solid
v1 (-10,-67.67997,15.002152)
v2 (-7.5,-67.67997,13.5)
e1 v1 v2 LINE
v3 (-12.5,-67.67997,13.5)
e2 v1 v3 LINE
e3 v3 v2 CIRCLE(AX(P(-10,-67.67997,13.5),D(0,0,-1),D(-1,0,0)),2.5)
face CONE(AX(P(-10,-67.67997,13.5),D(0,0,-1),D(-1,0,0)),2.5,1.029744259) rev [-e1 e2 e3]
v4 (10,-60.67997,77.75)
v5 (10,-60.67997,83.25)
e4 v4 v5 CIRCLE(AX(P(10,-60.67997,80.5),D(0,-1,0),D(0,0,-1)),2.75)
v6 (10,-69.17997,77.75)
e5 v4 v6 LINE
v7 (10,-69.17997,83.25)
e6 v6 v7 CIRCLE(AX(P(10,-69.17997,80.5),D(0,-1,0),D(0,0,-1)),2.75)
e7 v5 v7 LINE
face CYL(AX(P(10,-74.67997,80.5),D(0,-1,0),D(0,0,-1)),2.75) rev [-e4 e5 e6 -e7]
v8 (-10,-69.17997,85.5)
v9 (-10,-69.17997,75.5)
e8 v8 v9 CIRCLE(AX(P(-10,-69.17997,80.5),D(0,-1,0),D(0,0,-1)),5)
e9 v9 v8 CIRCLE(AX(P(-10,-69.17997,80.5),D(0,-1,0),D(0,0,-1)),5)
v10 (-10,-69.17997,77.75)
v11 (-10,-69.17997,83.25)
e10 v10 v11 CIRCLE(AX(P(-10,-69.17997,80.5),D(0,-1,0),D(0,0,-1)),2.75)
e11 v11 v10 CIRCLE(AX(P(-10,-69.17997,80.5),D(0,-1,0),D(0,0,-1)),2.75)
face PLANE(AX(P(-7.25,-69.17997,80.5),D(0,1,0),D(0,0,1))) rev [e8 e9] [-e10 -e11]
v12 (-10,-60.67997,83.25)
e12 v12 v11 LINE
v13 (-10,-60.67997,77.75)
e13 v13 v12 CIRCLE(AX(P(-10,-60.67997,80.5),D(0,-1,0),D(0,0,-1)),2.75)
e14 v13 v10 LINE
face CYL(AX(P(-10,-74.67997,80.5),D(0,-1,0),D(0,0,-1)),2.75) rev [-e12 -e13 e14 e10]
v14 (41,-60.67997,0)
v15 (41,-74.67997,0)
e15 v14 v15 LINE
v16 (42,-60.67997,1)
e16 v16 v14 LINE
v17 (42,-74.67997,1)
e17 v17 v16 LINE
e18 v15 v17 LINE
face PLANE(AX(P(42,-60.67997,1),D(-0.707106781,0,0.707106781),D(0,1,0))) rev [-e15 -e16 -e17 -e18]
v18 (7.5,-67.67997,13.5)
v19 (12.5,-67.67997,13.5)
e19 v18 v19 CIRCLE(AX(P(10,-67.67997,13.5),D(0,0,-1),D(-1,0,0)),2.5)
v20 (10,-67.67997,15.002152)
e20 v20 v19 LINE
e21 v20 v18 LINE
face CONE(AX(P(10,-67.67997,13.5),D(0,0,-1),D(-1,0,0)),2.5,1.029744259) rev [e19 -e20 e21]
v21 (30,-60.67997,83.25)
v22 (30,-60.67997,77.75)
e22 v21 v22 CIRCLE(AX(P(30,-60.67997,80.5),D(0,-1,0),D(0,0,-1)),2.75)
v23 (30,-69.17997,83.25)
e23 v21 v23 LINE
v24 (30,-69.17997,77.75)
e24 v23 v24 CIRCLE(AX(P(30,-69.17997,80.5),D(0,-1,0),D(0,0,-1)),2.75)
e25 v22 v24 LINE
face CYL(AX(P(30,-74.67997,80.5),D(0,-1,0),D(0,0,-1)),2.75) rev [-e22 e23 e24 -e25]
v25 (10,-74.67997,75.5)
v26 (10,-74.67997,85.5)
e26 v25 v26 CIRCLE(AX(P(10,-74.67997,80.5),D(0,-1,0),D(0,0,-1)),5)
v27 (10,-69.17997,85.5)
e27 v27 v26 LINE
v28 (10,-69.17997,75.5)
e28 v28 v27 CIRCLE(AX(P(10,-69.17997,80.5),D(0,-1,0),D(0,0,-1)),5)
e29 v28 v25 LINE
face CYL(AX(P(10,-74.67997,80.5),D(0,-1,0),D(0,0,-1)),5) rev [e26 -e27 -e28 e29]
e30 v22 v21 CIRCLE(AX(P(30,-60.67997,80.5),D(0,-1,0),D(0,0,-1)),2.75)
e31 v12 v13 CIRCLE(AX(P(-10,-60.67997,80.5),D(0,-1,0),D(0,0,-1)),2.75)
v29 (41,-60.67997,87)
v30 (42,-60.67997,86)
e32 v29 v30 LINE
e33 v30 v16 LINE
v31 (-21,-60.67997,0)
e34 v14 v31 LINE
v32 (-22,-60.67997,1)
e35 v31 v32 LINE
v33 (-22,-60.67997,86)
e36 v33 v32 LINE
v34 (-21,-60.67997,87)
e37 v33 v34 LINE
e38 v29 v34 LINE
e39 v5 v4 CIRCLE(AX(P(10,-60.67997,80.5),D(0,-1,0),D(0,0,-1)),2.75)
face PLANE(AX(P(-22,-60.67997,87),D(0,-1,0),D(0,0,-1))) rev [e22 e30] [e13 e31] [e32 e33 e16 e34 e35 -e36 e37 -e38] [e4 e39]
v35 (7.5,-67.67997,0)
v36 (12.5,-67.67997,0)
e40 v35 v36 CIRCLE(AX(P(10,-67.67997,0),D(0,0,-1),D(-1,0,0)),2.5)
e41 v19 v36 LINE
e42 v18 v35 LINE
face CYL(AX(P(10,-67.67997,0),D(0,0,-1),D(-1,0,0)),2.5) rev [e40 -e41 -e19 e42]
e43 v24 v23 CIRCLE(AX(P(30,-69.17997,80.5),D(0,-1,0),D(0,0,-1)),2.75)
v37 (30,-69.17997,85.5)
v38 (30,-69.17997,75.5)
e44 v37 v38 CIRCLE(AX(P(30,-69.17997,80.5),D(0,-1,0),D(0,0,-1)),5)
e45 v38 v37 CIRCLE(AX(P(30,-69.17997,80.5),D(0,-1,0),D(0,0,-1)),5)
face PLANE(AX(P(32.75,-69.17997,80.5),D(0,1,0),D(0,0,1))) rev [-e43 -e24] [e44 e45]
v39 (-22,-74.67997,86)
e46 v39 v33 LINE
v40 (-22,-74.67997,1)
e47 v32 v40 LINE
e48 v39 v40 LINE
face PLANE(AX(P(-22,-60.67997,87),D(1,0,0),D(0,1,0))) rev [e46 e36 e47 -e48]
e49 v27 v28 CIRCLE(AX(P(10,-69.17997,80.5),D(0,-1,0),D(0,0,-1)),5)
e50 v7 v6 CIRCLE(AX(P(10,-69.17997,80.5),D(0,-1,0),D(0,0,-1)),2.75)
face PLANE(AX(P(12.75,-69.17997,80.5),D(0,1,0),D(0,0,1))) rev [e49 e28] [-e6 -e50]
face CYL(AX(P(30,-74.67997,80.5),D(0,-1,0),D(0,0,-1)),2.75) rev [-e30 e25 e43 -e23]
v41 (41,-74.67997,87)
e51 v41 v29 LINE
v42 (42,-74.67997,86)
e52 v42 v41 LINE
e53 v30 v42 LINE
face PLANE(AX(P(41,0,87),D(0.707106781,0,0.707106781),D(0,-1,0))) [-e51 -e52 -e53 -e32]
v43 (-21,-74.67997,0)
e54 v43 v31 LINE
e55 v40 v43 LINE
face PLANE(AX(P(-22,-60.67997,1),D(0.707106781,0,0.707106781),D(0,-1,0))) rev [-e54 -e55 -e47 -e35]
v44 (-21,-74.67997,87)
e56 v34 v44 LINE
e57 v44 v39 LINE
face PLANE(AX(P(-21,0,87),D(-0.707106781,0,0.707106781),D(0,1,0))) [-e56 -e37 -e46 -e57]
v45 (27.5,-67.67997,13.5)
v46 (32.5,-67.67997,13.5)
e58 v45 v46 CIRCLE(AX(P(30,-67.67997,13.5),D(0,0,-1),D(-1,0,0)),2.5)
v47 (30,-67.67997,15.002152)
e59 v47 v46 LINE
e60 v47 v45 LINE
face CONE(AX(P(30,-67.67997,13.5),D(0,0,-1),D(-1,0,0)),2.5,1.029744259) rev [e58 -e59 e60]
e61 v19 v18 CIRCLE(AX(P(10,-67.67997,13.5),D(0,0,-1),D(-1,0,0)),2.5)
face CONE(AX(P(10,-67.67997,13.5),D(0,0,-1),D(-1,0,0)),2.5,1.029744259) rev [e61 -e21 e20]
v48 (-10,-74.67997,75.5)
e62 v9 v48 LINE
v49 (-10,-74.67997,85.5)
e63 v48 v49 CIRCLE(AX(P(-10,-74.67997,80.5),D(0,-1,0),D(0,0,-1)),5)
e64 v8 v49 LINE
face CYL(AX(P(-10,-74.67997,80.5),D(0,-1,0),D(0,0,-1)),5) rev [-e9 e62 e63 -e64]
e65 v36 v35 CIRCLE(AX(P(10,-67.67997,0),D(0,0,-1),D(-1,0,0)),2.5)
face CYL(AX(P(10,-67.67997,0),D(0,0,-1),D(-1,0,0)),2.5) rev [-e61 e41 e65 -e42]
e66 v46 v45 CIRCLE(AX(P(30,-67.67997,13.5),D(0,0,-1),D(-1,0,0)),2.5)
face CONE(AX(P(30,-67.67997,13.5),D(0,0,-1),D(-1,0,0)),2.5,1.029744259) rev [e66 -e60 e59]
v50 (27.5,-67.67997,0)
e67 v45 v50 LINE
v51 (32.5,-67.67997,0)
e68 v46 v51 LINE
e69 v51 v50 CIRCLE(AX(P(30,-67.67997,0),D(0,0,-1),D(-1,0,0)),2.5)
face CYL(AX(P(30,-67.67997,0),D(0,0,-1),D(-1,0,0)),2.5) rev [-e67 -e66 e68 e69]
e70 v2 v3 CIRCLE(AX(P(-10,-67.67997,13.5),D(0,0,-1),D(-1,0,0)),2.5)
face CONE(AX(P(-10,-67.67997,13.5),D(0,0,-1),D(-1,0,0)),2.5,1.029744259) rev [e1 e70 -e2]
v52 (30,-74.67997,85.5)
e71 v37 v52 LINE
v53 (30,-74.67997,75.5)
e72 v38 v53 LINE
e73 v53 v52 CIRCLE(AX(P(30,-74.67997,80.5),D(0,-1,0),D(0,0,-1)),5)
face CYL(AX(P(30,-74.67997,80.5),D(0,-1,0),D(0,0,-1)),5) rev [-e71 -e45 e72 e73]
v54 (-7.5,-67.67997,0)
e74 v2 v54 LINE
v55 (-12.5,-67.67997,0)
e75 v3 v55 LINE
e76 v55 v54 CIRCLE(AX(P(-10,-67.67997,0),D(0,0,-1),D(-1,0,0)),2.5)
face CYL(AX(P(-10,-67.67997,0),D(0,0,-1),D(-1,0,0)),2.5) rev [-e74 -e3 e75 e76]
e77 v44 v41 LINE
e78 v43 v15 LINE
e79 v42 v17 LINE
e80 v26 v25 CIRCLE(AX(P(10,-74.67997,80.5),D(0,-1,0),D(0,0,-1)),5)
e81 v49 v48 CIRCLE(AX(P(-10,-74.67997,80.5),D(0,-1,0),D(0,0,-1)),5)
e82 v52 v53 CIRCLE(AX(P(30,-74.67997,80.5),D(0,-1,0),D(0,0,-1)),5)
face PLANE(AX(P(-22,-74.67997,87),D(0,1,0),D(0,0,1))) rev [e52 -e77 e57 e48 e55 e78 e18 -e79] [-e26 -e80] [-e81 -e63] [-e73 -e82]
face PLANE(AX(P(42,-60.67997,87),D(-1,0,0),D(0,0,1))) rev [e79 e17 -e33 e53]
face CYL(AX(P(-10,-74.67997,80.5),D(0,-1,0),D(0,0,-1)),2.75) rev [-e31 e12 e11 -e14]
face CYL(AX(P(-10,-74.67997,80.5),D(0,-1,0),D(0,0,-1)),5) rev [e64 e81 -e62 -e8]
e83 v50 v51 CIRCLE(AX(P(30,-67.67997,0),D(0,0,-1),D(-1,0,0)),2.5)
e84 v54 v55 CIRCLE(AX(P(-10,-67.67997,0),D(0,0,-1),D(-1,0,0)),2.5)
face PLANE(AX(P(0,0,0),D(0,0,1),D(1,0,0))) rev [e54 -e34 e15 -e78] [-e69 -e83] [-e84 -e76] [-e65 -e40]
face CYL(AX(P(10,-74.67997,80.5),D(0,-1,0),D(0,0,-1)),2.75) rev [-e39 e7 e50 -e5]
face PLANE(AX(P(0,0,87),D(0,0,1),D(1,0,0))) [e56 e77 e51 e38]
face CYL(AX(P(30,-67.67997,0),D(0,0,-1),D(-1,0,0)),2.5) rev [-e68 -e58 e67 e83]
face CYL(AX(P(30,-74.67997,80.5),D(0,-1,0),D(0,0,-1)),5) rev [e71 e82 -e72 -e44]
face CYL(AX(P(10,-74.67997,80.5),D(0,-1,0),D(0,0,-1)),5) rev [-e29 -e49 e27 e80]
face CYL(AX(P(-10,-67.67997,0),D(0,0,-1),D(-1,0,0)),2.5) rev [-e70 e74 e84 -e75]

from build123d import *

# Parameters (mm, degrees)
SKETCH_1_W                  = 64
SKETCH_1_H                  = 14
EXTRUDE_1_DEPTH             = 87
HOLE_WIZARD_C_0_D           = 5.5
HOLE_WIZARD_C_0_CBORE_D     = 10
HOLE_WIZARD_C_0_CBORE_DEPTH = 5.5
HOLE_WIZARD_M6_1_D          = 5
HOLE_WIZARD_M6_1_DEPTH      = 13.5
HOLE_WIZARD_M6_1_TIP        = 1.502151548
CHAMFER_1_SIZE              = 1


with BuildPart() as part:
    # 草图1 → 凸台-拉伸1 (new body)
    with BuildSketch(Plane.XY):
        with Locations((10, -67.679969714)):
            Rectangle(SKETCH_1_W, SKETCH_1_H)
    extrude(amount=EXTRUDE_1_DEPTH)

    # 打孔尺寸根据六角头螺栓 C 级的类型0 (through all)
    with Locations(Plane(origin=(0, -74.679969714, 0), x_dir=(-1, 0, 0), z_dir=(0, -1, 0))):
        with Locations((10, -80.5), (-10, -80.5), (-30, -80.5)):
            CounterBoreHole(HOLE_WIZARD_C_0_D / 2, HOLE_WIZARD_C_0_CBORE_D / 2, HOLE_WIZARD_C_0_CBORE_DEPTH)

    # M6 螺纹孔1
    with Locations(Plane(origin=(0, 0, 0), x_dir=(-1, 0, 0), z_dir=(0, 0, -1))):
        with Locations((-30, -67.679969714), (-10, -67.679969714), (10, -67.679969714)):
            Hole(HOLE_WIZARD_M6_1_D / 2, depth=HOLE_WIZARD_M6_1_DEPTH)
            with Locations((0, 0, -(HOLE_WIZARD_M6_1_DEPTH + HOLE_WIZARD_M6_1_TIP / 2))):  # 118° drill point
                Cone(0, HOLE_WIZARD_M6_1_D / 2, HOLE_WIZARD_M6_1_TIP, mode=Mode.SUBTRACT)

    # 倒角1
    chamfer_1_edges = [part.edges().sort_by_distance(p)[0] for p in [
        (42, -67.679969714, 87),
        (-22, -67.679969714, 87),
        (42, -67.679969714, 0),
        (-22, -67.679969714, 0),
    ]]
    chamfer(chamfer_1_edges, length=CHAMFER_1_SIZE)


solid = part.part
